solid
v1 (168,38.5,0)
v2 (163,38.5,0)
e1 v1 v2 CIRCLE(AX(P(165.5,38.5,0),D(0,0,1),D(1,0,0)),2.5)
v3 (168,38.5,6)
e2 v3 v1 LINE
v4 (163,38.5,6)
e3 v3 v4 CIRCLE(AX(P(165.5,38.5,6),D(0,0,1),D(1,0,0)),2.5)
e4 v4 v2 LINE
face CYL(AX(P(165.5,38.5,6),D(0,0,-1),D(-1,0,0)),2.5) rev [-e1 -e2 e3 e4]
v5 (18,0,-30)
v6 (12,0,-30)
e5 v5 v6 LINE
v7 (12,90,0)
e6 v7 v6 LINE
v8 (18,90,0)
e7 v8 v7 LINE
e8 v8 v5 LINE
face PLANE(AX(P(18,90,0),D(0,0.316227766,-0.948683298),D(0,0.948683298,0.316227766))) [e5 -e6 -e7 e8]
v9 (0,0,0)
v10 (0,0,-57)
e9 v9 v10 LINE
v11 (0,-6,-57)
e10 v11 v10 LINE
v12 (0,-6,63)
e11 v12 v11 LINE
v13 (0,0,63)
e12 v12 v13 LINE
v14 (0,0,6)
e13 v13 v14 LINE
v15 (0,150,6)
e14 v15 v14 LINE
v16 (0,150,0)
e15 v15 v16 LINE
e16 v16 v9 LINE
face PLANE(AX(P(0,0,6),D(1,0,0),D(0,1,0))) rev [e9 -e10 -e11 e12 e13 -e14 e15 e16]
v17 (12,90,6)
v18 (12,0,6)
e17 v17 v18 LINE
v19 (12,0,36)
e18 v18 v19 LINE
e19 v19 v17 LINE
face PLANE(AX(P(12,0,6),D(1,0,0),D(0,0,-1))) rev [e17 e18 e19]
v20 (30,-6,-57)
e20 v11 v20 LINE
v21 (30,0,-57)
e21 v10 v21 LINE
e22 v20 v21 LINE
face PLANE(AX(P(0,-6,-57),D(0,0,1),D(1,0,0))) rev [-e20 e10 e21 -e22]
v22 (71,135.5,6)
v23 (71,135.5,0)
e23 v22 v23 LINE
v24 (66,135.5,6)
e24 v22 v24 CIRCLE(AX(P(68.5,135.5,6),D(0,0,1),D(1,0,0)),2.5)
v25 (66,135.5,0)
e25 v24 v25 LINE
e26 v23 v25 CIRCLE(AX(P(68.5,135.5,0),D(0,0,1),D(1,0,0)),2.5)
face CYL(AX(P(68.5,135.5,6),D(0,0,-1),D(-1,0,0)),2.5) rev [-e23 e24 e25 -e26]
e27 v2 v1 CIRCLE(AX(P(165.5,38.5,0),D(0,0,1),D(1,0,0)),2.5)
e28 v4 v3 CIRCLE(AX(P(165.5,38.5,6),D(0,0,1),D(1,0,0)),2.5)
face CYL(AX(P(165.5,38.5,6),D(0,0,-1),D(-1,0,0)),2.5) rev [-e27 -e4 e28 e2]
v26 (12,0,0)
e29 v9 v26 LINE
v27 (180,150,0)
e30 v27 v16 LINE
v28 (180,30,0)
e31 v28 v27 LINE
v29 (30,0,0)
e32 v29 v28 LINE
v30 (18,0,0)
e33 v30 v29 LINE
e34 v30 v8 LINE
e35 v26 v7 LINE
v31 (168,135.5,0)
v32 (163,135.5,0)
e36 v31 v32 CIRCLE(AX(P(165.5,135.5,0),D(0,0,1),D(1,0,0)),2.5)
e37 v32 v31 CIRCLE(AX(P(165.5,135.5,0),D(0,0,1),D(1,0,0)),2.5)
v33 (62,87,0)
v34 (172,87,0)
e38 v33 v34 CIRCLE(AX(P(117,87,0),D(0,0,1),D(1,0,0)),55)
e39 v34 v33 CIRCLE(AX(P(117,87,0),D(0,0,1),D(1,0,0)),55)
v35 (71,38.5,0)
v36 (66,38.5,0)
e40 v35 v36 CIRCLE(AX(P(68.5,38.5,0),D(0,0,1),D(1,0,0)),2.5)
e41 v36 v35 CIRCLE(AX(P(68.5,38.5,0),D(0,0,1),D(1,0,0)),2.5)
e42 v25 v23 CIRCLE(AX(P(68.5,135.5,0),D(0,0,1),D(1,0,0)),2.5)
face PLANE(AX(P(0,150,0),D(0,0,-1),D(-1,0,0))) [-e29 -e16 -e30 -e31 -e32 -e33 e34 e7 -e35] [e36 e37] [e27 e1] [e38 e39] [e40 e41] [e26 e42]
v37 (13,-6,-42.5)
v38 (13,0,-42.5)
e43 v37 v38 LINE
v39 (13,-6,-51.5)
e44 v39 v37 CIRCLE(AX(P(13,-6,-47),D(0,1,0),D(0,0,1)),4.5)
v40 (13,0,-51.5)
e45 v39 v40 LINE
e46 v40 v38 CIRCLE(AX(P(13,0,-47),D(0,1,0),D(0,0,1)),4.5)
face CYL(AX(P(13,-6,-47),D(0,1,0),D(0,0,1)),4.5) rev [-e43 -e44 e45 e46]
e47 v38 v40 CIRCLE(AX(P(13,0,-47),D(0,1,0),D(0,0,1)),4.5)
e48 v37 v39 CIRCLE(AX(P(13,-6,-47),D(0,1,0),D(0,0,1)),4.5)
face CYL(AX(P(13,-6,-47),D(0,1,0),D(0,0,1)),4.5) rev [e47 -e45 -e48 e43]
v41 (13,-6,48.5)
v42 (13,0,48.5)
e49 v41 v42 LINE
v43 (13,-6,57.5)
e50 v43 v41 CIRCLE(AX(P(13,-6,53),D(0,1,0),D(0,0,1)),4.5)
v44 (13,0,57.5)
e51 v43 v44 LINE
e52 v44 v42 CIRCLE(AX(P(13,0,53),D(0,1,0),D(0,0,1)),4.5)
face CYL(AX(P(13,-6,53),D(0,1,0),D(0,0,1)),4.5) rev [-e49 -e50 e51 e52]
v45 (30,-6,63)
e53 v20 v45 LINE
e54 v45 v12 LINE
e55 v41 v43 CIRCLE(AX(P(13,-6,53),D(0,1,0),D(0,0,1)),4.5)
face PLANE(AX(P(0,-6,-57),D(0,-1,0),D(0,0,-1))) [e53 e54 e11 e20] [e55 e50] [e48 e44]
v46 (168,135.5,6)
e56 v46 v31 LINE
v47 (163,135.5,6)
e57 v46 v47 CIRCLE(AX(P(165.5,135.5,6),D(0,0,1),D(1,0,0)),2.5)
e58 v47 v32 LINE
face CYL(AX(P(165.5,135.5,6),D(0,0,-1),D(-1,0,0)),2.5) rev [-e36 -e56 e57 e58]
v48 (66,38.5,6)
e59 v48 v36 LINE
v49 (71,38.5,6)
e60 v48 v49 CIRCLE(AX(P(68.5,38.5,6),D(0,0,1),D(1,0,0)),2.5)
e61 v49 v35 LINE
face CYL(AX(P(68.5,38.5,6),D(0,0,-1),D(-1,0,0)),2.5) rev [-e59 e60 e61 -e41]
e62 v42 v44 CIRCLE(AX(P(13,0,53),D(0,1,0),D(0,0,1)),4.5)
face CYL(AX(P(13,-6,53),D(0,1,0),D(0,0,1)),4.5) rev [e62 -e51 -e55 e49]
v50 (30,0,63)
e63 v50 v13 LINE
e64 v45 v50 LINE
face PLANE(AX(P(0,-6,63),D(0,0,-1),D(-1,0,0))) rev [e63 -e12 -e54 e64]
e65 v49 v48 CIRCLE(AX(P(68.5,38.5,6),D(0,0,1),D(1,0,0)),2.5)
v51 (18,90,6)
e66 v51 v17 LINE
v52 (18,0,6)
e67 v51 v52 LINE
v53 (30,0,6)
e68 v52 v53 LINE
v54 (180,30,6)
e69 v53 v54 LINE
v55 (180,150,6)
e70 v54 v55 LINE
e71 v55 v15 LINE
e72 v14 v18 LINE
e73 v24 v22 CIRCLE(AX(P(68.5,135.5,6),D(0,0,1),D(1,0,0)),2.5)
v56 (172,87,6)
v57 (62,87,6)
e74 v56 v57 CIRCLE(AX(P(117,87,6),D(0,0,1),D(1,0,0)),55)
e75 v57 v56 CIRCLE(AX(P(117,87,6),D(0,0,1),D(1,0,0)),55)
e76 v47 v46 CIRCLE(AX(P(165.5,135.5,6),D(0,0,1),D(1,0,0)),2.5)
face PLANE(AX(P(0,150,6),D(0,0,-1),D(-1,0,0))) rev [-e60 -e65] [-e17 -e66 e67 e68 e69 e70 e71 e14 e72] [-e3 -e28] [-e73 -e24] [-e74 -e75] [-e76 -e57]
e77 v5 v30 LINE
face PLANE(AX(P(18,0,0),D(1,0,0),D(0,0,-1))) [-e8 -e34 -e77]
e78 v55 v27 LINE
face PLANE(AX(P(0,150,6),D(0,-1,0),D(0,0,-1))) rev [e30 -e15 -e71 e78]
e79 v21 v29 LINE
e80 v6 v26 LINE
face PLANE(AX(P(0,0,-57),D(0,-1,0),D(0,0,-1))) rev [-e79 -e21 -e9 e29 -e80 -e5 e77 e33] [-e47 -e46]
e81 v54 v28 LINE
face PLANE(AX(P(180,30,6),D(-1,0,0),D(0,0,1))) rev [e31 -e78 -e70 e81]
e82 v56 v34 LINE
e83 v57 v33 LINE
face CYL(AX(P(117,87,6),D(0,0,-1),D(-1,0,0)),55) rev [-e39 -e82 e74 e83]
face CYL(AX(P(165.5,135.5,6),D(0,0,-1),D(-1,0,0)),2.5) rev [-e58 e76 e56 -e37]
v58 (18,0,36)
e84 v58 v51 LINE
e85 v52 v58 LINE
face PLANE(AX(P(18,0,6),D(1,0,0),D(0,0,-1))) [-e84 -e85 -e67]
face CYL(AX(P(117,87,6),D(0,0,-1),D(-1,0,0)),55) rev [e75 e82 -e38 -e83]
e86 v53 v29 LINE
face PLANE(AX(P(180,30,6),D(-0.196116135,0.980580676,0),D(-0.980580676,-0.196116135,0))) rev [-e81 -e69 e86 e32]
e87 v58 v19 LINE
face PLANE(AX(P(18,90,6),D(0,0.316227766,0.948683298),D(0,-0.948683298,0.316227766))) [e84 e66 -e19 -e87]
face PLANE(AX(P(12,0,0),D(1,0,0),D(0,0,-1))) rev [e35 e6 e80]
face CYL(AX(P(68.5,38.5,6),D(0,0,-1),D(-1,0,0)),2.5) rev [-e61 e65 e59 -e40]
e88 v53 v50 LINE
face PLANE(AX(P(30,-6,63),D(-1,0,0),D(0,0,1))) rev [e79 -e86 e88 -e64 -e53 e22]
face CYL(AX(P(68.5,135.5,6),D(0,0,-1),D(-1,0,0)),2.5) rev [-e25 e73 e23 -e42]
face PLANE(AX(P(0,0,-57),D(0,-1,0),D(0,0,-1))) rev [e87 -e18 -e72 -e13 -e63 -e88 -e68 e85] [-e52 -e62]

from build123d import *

# Parameters (mm, degrees)
SKETCH_1_R           = 2.5
SKETCH_1_R_2         = 55
EXTRUDE_1_DEPTH      = 6
SKETCH_4_W           = 30
SKETCH_4_H           = 120
EXTRUDE_3_DEPTH      = 6
SKETCH_5_R           = 4.5
CUT_EXTRUDE_1_DEPTH  = 6
EXTRUDE_4_DEPTH      = 3
EXTRUDE_4_DEPTH_BACK = 3


with BuildPart() as part:
    # 草图1 → 凸台-拉伸1 (new body)
    with BuildSketch(Plane.XY):
        Polygon((0, 0), (30, 0), (180, 30), (180, 150), (0, 150), align=None)
        with Locations((165.5, 135.5)):
            Circle(SKETCH_1_R, mode=Mode.SUBTRACT)
        with Locations((68.5, 135.5)):
            Circle(SKETCH_1_R, mode=Mode.SUBTRACT)
        with Locations((165.5, 38.5)):
            Circle(SKETCH_1_R, mode=Mode.SUBTRACT)
        with Locations((68.5, 38.5)):
            Circle(SKETCH_1_R, mode=Mode.SUBTRACT)
        with Locations((117, 87)):
            Circle(SKETCH_1_R_2, mode=Mode.SUBTRACT)
    extrude(amount=EXTRUDE_1_DEPTH)

    # 草图4 → 凸台-拉伸3 (add)
    with BuildSketch(Plane.XZ):
        with Locations((15, 3)):
            Rectangle(SKETCH_4_W, SKETCH_4_H)
    extrude(amount=EXTRUDE_3_DEPTH)

    # 草图5 → 切除-拉伸1 (cut)
    with BuildSketch(Plane(origin=(0, 0, 0), x_dir=(1, 0, 0), z_dir=(0, 1, 0))):
        with Locations(Location((13, 47, 0), (0, 0, 270))):
            Circle(SKETCH_5_R)
        with Locations(Location((13, -53, 0), (0, 0, 270))):
            Circle(SKETCH_5_R)
    extrude(amount=-CUT_EXTRUDE_1_DEPTH, mode=Mode.SUBTRACT)

    # 草图6 → 凸台-拉伸4 (add, two sides: drawn at the far end of the back side and taken through both)
    with BuildSketch(Plane.ZY.offset(-15).offset(-EXTRUDE_4_DEPTH_BACK)):
        Polygon((0, 90), (-30, 0), (0, 0), align=None)
        Polygon((6, 0), (6, 90), (36, 0), align=None)
    extrude(amount=EXTRUDE_4_DEPTH + EXTRUDE_4_DEPTH_BACK)


solid = part.part
